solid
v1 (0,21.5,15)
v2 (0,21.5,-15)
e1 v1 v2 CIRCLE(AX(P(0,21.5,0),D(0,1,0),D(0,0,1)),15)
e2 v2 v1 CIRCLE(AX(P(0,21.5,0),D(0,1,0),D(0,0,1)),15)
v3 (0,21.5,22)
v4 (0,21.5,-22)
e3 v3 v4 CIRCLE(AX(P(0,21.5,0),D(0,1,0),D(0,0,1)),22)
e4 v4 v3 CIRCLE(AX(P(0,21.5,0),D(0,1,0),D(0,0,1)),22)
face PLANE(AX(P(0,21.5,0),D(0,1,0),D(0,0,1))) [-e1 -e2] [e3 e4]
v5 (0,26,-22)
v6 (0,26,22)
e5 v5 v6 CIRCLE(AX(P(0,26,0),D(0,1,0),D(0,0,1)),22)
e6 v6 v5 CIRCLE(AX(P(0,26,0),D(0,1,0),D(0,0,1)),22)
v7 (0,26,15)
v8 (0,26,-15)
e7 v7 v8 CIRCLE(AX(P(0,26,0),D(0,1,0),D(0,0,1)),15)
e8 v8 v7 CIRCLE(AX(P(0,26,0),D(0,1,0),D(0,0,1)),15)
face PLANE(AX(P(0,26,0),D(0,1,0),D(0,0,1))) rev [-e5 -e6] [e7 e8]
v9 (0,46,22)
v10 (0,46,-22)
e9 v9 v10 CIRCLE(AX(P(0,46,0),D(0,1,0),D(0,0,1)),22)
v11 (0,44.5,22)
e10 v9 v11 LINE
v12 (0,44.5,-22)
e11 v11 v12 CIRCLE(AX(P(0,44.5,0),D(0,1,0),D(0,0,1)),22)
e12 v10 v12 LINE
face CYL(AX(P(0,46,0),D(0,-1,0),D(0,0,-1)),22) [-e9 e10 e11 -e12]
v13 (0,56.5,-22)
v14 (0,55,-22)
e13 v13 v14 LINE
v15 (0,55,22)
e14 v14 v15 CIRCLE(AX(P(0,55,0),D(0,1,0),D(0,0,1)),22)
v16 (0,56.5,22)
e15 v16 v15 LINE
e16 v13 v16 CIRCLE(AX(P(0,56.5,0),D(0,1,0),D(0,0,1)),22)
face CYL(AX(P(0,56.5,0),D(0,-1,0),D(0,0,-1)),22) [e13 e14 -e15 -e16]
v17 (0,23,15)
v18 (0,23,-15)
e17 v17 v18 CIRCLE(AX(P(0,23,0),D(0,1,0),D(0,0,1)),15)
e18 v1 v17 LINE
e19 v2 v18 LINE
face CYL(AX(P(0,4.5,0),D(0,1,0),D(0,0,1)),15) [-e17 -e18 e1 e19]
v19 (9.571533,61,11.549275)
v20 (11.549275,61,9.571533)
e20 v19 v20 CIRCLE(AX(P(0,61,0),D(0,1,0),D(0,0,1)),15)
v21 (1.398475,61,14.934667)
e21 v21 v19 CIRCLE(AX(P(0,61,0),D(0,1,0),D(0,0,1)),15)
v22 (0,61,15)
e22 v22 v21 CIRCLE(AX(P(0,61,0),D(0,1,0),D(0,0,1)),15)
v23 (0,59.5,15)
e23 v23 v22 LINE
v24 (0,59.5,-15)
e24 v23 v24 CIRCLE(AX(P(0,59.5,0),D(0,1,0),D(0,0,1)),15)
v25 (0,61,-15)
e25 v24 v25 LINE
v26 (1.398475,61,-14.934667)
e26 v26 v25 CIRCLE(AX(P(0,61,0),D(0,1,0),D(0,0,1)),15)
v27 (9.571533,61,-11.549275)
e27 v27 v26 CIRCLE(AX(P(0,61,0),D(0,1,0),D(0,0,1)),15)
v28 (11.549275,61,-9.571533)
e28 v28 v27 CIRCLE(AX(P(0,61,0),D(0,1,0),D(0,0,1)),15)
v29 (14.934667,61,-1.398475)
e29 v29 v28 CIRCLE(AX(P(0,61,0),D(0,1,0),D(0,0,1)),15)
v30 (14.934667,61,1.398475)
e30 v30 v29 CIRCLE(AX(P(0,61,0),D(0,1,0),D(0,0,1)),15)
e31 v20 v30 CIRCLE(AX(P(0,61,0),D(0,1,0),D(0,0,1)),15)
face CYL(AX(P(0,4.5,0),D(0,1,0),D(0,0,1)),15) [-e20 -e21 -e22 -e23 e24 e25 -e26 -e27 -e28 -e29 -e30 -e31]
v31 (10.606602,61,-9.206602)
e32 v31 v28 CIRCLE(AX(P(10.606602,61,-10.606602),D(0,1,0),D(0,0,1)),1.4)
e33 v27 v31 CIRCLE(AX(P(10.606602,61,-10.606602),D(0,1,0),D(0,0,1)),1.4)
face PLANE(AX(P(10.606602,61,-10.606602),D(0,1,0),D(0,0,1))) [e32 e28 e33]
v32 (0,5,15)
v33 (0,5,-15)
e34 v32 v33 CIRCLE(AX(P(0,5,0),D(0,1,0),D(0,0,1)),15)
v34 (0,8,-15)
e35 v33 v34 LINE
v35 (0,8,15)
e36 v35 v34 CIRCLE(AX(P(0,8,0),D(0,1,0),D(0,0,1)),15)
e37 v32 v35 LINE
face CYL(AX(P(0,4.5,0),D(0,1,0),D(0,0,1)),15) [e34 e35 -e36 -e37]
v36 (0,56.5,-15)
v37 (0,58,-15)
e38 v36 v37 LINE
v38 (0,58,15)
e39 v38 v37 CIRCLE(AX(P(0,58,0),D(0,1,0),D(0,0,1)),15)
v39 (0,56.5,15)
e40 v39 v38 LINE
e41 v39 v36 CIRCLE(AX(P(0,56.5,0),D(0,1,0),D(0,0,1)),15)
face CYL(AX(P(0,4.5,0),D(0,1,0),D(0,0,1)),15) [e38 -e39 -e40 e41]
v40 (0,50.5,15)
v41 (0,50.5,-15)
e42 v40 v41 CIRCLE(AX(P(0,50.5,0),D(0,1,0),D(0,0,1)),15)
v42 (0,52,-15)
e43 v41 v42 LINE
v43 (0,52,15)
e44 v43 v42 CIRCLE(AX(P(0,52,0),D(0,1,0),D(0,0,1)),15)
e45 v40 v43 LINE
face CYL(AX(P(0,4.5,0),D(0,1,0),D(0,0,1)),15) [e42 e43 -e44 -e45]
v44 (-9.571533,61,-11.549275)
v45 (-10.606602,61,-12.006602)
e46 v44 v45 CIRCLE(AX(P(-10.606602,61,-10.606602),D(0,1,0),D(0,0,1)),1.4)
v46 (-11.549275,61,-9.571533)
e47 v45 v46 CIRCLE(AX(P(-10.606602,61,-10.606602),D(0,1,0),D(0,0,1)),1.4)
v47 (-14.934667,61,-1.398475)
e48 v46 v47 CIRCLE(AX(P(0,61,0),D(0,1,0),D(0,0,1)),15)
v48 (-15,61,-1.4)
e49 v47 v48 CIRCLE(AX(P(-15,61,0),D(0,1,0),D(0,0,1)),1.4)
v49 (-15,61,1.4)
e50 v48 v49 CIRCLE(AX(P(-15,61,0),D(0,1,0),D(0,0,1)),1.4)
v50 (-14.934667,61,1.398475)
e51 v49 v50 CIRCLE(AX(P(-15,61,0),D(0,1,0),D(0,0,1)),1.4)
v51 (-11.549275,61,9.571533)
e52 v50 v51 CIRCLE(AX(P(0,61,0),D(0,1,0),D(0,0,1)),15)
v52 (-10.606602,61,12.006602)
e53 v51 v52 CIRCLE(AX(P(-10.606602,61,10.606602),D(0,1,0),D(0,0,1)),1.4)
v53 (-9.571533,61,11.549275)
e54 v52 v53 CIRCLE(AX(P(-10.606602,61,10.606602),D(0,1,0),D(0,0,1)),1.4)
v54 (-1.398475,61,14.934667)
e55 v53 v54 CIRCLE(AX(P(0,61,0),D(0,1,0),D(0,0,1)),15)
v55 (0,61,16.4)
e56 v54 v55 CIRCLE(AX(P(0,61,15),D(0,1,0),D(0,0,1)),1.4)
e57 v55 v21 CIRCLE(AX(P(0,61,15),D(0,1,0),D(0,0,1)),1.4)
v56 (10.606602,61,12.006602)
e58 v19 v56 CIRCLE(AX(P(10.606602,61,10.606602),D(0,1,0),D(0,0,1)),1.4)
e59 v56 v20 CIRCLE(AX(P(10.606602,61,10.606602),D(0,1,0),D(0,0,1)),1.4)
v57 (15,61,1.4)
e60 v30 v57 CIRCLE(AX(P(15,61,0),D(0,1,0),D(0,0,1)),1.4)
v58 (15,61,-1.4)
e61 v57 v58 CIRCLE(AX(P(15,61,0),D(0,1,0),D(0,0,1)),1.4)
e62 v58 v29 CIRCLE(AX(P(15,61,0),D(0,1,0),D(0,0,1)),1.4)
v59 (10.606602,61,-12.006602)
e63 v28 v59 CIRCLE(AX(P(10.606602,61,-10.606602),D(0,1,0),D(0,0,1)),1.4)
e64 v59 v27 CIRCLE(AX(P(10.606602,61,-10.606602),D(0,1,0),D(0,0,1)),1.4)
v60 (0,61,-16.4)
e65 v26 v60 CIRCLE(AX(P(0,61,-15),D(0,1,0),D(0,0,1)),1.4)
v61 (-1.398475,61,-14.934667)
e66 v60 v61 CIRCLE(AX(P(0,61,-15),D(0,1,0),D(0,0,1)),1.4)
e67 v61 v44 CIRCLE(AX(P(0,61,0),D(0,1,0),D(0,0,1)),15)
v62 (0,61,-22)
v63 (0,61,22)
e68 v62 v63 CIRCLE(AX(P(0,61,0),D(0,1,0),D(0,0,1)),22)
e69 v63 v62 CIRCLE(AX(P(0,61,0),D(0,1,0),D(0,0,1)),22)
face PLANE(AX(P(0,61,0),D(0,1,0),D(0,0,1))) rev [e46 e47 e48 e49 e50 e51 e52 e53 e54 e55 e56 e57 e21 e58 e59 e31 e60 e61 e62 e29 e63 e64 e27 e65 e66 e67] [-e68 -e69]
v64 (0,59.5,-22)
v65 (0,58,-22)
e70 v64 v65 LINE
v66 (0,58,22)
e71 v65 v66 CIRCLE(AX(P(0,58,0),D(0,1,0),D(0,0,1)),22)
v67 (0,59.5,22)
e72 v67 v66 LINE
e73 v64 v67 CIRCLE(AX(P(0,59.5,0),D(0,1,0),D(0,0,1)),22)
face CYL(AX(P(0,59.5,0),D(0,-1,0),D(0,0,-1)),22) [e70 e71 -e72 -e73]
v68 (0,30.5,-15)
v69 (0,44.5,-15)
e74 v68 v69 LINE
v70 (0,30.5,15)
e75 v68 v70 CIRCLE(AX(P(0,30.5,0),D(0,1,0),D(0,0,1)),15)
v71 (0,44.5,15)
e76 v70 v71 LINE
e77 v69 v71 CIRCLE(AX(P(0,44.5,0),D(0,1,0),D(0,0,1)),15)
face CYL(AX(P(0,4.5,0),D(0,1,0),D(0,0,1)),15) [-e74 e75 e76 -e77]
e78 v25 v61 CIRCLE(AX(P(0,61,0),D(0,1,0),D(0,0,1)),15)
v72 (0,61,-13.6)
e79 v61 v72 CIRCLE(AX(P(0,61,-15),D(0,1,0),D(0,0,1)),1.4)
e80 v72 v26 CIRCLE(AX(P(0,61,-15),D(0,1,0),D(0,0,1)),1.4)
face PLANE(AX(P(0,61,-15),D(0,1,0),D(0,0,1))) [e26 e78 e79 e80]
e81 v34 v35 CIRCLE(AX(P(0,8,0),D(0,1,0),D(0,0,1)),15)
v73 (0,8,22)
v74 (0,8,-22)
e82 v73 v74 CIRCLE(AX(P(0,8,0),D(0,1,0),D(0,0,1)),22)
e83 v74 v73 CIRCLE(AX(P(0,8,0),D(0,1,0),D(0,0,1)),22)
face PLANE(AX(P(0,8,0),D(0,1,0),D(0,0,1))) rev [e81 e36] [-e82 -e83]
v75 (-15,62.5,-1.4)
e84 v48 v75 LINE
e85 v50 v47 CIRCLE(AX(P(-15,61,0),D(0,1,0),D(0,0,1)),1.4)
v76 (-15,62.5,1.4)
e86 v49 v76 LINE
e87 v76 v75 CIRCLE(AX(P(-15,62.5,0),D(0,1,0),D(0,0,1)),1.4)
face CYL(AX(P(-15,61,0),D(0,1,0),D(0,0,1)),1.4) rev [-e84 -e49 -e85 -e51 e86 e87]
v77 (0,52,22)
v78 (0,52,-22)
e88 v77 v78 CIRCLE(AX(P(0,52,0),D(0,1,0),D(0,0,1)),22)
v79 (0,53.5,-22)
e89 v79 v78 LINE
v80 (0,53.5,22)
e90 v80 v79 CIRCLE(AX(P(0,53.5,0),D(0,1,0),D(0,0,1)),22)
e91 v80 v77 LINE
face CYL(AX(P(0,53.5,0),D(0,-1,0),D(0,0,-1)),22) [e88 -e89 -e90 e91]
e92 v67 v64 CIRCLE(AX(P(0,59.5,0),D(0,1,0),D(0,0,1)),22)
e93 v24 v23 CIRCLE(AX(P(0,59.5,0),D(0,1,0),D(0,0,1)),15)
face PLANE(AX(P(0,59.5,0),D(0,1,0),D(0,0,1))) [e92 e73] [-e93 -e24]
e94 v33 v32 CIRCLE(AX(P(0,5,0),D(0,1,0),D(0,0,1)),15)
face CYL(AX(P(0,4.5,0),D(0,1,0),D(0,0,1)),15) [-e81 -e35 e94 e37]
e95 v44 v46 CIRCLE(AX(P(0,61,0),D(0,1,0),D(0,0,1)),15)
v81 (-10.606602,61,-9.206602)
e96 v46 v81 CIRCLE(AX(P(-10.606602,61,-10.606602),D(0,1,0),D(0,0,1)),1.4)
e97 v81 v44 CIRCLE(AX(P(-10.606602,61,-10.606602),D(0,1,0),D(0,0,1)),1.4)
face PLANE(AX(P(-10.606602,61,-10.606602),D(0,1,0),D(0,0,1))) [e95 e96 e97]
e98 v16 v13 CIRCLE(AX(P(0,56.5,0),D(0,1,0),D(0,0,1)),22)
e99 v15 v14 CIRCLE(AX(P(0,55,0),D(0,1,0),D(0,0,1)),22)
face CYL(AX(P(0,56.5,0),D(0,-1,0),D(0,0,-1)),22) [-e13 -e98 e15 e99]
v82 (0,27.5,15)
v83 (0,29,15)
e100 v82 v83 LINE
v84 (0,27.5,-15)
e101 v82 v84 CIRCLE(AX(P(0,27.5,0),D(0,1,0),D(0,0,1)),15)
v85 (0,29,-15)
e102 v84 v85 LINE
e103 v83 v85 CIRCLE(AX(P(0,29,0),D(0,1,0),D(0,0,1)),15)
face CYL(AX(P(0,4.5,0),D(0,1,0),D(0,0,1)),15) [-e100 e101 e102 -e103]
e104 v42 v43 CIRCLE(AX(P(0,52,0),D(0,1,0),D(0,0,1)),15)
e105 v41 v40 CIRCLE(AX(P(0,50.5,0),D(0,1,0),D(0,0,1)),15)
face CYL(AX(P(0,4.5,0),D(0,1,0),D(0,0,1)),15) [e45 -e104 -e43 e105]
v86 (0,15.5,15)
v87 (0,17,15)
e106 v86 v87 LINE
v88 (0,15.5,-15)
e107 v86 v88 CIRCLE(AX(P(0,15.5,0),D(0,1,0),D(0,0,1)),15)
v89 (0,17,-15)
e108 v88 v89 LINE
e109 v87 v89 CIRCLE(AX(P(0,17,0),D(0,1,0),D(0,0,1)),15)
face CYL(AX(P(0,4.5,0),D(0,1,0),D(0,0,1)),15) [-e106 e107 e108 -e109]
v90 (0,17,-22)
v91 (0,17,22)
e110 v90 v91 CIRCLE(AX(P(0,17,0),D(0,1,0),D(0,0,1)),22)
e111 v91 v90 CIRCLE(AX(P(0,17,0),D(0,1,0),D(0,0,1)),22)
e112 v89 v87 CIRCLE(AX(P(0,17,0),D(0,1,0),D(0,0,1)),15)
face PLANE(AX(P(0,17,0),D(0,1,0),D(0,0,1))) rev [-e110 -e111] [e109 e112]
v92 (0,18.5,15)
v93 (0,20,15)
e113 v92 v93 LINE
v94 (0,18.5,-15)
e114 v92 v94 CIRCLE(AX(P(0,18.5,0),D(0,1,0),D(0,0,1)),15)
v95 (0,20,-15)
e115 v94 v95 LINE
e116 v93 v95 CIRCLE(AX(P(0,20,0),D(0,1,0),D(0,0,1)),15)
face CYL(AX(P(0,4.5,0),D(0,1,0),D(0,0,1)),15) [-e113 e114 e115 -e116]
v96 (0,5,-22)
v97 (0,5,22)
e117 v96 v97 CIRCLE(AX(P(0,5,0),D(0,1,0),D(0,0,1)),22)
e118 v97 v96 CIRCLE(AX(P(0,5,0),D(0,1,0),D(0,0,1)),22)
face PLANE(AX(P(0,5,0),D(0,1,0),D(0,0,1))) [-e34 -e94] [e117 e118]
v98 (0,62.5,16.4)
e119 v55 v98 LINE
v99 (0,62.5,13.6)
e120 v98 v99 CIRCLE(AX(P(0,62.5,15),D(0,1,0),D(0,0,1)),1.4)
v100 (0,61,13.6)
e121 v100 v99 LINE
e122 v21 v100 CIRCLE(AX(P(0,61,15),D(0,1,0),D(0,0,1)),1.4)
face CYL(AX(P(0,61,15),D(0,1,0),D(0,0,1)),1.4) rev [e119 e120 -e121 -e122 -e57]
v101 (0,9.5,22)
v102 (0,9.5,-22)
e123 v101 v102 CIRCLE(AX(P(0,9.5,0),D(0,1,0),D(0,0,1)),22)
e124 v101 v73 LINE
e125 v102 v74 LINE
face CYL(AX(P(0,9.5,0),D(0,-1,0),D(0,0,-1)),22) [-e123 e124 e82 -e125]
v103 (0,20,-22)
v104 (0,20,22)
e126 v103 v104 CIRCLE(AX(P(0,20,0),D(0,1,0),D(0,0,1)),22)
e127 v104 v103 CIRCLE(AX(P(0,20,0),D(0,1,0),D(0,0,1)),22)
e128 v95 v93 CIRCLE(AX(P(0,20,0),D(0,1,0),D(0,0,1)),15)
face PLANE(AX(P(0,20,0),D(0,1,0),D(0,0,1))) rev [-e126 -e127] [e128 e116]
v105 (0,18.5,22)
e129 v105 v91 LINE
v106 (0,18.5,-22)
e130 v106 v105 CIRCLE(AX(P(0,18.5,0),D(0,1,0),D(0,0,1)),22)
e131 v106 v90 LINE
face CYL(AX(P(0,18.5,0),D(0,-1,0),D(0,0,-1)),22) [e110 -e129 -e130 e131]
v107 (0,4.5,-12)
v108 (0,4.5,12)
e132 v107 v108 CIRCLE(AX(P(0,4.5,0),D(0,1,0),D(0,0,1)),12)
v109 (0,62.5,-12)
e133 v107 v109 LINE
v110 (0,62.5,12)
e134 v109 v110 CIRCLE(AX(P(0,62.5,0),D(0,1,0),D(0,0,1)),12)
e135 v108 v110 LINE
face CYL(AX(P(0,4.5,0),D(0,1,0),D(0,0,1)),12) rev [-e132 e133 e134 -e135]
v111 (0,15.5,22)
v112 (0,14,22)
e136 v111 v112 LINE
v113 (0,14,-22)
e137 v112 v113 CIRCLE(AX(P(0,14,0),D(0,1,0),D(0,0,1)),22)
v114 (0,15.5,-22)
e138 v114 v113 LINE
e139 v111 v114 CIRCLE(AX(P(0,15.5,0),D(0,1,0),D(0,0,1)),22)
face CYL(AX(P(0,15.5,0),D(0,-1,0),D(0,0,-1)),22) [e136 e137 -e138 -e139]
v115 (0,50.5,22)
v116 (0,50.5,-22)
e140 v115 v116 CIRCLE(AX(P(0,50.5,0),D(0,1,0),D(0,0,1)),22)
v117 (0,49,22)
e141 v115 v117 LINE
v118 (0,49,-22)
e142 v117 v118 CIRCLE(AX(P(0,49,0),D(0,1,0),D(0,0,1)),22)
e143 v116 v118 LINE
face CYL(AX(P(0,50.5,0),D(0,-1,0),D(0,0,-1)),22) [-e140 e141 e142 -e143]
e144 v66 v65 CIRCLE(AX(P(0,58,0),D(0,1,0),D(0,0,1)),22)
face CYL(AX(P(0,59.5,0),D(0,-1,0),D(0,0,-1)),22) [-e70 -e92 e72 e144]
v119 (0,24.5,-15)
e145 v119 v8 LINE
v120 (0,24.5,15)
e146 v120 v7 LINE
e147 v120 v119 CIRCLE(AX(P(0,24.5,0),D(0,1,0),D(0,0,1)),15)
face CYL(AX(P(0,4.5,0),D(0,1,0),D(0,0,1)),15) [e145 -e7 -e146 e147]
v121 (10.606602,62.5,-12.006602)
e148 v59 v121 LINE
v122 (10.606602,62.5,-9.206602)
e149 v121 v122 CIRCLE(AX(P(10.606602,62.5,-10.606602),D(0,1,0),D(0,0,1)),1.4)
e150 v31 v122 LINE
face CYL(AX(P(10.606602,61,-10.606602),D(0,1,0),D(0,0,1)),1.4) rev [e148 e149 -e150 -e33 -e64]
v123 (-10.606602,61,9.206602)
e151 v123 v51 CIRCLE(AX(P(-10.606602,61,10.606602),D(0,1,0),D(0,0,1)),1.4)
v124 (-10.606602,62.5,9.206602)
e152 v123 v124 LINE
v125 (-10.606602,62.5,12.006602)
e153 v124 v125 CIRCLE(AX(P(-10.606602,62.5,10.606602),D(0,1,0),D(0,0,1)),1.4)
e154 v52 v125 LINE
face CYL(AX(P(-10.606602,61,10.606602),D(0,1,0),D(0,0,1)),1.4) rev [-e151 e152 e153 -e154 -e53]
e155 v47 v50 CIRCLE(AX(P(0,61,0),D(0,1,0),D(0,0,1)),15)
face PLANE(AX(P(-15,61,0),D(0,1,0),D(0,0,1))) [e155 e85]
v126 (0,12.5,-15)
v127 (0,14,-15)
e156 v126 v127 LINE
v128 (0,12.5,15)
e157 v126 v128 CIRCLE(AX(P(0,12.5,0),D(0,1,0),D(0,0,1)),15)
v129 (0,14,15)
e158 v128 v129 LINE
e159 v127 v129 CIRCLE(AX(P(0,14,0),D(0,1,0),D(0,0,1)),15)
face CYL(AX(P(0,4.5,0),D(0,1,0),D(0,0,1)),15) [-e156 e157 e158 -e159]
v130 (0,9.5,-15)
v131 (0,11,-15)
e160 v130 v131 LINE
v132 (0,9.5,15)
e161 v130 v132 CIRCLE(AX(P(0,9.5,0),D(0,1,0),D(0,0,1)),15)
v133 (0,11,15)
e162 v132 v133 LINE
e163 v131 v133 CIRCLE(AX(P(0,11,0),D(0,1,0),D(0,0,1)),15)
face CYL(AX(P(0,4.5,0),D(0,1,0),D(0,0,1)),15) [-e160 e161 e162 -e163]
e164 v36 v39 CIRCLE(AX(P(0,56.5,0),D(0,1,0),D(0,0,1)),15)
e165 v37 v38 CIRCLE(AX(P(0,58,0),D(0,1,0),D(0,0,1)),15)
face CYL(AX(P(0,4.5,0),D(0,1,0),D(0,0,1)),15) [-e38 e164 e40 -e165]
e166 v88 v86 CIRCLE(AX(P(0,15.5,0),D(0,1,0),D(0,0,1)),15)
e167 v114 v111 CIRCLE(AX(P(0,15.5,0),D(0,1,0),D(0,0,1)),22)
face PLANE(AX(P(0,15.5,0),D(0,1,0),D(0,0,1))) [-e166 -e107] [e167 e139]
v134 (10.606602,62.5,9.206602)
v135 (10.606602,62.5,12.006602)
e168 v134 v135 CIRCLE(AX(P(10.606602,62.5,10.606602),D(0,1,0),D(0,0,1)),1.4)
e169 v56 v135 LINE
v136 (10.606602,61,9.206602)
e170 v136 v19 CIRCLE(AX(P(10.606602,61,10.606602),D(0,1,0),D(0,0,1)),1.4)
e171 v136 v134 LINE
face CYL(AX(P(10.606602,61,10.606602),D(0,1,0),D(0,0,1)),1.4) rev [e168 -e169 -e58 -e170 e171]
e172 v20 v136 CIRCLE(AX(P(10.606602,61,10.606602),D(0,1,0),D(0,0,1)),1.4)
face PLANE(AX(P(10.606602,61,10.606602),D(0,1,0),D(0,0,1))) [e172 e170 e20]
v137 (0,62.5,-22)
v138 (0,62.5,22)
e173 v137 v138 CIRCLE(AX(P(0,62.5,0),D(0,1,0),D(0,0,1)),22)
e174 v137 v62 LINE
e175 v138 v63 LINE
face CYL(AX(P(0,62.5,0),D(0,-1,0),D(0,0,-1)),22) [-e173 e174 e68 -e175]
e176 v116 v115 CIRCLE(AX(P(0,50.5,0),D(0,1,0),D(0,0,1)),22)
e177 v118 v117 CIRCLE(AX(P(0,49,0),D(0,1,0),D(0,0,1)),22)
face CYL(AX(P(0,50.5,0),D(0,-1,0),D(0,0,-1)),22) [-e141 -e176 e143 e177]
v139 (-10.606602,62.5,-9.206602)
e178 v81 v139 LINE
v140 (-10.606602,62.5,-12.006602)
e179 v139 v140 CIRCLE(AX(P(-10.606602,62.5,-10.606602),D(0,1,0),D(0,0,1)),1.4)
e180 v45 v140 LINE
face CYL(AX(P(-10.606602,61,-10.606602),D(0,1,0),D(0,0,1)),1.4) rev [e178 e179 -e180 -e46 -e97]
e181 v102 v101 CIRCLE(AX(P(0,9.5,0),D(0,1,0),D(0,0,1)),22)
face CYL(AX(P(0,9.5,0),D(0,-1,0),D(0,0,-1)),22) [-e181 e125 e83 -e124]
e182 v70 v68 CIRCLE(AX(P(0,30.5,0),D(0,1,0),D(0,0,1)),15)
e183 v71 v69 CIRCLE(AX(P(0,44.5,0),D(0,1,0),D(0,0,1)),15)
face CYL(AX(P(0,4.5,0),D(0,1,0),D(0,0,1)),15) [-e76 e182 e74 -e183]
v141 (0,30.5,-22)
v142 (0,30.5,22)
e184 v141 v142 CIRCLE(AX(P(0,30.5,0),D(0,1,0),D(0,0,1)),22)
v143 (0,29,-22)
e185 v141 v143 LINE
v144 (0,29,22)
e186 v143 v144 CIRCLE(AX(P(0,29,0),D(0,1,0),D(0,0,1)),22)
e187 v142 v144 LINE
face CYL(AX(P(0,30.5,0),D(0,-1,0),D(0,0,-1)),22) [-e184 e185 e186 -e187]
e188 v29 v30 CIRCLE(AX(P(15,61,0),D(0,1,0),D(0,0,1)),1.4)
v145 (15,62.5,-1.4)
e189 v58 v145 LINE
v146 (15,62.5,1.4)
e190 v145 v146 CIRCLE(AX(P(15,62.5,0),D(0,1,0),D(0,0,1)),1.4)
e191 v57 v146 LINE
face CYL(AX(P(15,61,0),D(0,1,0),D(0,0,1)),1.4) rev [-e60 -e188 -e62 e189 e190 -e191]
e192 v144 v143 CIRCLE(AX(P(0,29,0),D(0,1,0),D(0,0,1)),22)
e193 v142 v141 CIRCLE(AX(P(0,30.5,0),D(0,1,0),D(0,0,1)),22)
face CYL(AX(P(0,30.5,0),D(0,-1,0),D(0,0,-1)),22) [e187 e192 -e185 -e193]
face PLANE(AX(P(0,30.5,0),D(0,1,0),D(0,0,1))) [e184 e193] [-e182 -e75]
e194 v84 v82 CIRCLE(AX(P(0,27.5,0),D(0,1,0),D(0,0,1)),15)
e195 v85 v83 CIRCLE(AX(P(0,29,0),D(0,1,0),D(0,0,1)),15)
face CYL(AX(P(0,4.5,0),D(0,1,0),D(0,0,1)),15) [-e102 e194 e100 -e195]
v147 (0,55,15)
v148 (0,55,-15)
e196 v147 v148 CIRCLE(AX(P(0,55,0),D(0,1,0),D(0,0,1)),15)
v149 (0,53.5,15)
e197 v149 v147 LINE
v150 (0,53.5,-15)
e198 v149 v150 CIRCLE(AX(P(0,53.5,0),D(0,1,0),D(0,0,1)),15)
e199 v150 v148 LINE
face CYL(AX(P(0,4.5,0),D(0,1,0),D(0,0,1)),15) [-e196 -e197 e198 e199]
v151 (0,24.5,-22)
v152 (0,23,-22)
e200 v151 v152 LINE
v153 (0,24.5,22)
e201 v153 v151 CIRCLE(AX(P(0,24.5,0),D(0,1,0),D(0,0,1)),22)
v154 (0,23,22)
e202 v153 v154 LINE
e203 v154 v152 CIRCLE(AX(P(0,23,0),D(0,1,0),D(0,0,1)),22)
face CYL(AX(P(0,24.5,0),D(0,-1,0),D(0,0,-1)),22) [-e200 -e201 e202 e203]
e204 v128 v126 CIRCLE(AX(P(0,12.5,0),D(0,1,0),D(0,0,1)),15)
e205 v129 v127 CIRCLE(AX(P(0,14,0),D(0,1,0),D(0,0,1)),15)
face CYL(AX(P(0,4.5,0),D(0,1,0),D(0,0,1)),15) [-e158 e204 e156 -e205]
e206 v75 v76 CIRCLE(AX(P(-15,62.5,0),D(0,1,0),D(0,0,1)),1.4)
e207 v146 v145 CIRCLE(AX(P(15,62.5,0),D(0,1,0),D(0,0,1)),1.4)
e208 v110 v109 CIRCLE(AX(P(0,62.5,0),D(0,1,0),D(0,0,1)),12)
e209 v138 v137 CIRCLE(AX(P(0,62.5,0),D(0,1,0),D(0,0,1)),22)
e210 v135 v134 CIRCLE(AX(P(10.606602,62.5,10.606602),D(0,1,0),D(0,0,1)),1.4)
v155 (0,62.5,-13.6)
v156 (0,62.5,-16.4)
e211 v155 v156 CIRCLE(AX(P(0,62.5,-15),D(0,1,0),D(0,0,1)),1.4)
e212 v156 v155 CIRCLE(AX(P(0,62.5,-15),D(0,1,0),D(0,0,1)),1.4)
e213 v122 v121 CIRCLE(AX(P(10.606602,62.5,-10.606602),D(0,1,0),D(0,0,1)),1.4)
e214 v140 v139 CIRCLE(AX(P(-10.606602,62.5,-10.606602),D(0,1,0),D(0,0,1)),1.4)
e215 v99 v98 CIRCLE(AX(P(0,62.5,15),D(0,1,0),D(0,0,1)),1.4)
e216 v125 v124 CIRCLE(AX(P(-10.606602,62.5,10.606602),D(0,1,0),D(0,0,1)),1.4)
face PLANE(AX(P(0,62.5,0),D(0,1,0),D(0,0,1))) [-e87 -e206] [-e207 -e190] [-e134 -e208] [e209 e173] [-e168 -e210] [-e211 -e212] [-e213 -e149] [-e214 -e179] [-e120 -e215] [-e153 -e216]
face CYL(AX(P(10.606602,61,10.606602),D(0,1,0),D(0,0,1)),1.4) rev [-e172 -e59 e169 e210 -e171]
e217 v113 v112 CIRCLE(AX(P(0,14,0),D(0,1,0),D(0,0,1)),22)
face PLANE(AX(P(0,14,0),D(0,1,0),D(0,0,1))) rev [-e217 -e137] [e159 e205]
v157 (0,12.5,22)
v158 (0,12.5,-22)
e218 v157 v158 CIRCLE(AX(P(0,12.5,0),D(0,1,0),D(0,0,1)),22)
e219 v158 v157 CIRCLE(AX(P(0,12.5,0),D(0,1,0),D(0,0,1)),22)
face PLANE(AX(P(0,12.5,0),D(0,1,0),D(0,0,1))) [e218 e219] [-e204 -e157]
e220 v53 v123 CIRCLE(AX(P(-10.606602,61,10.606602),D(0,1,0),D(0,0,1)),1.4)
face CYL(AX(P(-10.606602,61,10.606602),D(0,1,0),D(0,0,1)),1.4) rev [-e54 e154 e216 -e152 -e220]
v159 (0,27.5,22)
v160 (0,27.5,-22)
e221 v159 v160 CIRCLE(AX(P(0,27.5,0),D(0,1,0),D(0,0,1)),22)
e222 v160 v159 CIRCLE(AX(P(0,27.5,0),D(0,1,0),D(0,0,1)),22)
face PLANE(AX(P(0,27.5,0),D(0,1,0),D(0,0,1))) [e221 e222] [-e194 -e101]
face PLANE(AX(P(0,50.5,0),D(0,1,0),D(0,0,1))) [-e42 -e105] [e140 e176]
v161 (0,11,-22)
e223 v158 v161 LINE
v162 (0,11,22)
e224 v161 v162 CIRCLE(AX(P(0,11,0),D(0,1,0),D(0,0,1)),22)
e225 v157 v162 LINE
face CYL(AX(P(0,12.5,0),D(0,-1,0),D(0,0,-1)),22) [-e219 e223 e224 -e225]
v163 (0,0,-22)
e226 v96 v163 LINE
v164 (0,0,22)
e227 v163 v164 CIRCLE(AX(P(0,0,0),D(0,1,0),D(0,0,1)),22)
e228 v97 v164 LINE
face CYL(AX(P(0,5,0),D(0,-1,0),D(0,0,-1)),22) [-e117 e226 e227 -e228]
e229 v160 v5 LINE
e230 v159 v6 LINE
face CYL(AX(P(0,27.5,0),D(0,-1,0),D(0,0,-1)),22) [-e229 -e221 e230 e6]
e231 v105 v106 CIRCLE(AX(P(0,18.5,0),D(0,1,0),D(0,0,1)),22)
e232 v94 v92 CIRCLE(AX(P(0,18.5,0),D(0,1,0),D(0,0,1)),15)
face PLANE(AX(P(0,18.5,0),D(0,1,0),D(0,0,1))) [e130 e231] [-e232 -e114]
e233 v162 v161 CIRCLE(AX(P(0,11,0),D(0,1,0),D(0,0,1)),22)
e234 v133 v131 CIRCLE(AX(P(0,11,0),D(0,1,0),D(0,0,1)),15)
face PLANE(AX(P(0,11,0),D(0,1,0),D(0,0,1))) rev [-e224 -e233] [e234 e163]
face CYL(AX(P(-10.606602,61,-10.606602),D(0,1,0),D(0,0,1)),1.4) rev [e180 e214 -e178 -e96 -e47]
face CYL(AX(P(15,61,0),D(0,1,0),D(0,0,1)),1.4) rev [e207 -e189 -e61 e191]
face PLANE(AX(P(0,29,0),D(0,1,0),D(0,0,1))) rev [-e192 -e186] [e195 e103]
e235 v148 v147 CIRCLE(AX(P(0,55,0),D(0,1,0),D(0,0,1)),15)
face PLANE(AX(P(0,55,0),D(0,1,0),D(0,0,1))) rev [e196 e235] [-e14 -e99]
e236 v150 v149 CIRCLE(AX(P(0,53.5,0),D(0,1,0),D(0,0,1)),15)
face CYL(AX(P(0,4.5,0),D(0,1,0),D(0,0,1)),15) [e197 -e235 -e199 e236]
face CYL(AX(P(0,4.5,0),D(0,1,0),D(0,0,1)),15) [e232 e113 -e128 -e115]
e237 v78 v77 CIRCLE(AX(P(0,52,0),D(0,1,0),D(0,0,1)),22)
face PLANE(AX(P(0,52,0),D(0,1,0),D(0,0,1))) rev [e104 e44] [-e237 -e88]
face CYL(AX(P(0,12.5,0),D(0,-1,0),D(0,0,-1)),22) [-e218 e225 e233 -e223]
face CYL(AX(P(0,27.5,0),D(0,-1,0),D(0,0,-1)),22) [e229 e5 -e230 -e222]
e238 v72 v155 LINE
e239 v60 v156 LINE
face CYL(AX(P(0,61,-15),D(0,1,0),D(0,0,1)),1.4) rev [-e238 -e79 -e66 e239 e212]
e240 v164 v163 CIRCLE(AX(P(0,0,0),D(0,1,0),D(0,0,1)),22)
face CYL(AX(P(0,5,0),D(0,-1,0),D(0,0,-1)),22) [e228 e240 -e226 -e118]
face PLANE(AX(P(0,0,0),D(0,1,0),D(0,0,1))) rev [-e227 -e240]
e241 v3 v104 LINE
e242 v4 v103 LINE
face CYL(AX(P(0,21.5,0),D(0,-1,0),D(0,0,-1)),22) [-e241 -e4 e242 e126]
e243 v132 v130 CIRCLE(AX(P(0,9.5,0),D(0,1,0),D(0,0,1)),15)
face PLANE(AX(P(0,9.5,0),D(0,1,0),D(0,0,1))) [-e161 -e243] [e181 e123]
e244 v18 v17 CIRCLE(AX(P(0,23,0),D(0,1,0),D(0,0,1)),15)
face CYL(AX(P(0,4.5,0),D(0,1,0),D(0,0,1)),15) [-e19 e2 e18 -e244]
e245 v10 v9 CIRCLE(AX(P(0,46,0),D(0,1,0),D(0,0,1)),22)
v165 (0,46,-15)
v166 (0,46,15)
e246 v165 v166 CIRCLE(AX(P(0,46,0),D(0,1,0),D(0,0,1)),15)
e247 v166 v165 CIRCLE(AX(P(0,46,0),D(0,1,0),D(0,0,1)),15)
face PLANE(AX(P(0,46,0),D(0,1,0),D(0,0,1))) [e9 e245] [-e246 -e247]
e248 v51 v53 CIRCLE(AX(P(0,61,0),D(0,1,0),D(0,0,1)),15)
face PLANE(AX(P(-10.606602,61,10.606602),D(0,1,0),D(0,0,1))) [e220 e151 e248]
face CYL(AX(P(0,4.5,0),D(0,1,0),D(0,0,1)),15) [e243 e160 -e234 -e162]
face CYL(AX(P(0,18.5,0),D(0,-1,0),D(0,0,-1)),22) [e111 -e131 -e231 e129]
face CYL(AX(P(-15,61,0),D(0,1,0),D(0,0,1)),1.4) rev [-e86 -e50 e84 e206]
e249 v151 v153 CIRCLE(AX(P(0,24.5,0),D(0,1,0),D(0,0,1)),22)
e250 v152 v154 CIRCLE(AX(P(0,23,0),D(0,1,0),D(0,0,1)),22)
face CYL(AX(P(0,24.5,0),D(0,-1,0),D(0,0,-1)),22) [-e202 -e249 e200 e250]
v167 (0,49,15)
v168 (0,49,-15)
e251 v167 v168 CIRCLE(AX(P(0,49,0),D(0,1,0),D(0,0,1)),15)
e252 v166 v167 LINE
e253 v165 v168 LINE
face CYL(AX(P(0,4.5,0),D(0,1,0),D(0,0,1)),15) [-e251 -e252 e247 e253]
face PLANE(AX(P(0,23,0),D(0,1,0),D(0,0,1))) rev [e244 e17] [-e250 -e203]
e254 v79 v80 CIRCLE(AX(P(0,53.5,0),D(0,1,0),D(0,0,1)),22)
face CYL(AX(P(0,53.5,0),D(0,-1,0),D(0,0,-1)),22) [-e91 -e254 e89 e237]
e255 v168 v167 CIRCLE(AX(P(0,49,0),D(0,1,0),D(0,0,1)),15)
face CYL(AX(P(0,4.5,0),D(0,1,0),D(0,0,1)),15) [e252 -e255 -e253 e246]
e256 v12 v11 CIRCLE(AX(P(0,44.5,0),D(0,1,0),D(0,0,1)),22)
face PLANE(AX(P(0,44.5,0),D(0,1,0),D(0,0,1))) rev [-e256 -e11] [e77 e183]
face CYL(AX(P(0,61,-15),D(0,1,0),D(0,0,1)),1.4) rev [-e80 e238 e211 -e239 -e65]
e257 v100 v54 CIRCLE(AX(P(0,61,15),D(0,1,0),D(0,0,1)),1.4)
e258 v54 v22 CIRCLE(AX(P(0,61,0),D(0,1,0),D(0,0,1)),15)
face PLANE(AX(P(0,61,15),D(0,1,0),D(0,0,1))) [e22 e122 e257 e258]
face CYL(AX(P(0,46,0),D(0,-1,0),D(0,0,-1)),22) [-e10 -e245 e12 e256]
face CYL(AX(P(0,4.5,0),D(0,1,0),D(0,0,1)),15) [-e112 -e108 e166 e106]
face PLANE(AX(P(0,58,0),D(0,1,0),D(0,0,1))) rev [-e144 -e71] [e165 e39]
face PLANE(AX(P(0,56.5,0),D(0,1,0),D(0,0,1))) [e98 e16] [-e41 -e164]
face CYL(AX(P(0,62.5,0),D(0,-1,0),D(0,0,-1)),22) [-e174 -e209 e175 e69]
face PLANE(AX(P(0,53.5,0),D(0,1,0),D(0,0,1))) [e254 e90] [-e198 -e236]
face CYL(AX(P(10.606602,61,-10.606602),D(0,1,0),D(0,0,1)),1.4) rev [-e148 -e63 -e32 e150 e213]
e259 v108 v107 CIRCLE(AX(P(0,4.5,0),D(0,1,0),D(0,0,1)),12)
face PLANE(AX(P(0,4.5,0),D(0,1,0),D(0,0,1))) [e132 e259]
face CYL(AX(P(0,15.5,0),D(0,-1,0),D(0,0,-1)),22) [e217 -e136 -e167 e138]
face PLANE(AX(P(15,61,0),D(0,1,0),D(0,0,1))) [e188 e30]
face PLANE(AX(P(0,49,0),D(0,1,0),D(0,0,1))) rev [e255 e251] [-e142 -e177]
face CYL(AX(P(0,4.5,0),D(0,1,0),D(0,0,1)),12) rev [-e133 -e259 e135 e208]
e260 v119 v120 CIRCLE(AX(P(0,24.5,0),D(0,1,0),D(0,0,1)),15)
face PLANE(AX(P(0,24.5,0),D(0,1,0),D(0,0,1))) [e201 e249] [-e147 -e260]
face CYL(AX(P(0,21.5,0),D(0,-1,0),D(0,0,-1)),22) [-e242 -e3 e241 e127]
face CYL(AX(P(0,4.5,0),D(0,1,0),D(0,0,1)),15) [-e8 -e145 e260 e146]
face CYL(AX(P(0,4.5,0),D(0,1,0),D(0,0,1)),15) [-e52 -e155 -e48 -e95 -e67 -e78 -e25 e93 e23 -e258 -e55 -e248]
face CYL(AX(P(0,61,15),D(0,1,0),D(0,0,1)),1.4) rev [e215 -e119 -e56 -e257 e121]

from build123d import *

# Parameters (mm, degrees)
BASE_DISC_SKETCH_R     = 22
BASE_DISC_DEPTH        = 5
LOWER_FIN_1_SKETCH_R   = 22
LOWER_FIN_1_DEPTH      = 1.5
LOWER_FIN_2_SKETCH_R   = 22
LOWER_FIN_2_DEPTH      = 1.5
LOWER_FIN_3_SKETCH_R   = 22
LOWER_FIN_3_DEPTH      = 1.5
LOWER_FIN_4_SKETCH_R   = 22
LOWER_FIN_4_DEPTH      = 1.5
LOWER_FIN_5_SKETCH_R   = 22
LOWER_FIN_5_DEPTH      = 1.5
LOWER_FIN_6_SKETCH_R   = 22
LOWER_FIN_6_DEPTH      = 1.5
LOWER_FIN_7_SKETCH_R   = 22
LOWER_FIN_7_DEPTH      = 1.5
LOWER_FIN_8_SKETCH_R   = 22
LOWER_FIN_8_DEPTH      = 1.5
UPPER_FIN_1_SKETCH_R   = 22
UPPER_FIN_1_DEPTH      = 1.5
UPPER_FIN_2_SKETCH_R   = 22
UPPER_FIN_2_DEPTH      = 1.5
UPPER_FIN_3_SKETCH_R   = 22
UPPER_FIN_3_DEPTH      = 1.5
UPPER_FIN_4_SKETCH_R   = 22
UPPER_FIN_4_DEPTH      = 1.5
UPPER_FIN_5_SKETCH_R   = 22
UPPER_FIN_5_DEPTH      = 1.5
UPPER_FIN_6_SKETCH_R   = 22
UPPER_FIN_6_DEPTH      = 1.5
CORE_BOSS_SKETCH_R     = 12
CORE_BOSS_58MM_DEPTH   = 58
HUB_BOSS_SKETCH_R      = 15
HUB_BOSS_58MM_DEPTH    = 58
CENTRAL_BORE_SKETCH_R  = 12
CENTRAL_BORE_DEPTH     = 58
BOLT_HOLES_8X_SKETCH_R = 1.4
BOLT_HOLES_8X_DEPTH    = 1.5


with BuildPart() as part:
    # Base Disc Sketch → Base Disc (new body)
    with BuildSketch(Plane(origin=(0, 0, 0), x_dir=(1, 0, 0), z_dir=(0, 1, 0))):
        with Locations(Location((0, 0, 0), (0, 0, 270))):
            Circle(BASE_DISC_SKETCH_R)
    extrude(amount=BASE_DISC_DEPTH)



with BuildPart() as body_2:
    # Lower Fin 1 Sketch → Lower Fin 1 (new body)
    with BuildSketch(Plane(origin=(0, 8, 0), x_dir=(1, 0, 0), z_dir=(0, 1, 0))):
        with Locations(Location((0, 0, 0), (0, 0, 270))):
            Circle(LOWER_FIN_1_SKETCH_R)
    extrude(amount=LOWER_FIN_1_DEPTH)


with BuildPart() as body_3:
    # Lower Fin 2 Sketch → Lower Fin 2 (new body)
    with BuildSketch(Plane(origin=(0, 11, 0), x_dir=(1, 0, 0), z_dir=(0, 1, 0))):
        with Locations(Location((0, 0, 0), (0, 0, 270))):
            Circle(LOWER_FIN_2_SKETCH_R)
    extrude(amount=LOWER_FIN_2_DEPTH)


with BuildPart() as body_4:
    # Lower Fin 3 Sketch → Lower Fin 3 (new body)
    with BuildSketch(Plane(origin=(0, 14, 0), x_dir=(1, 0, 0), z_dir=(0, 1, 0))):
        with Locations(Location((0, 0, 0), (0, 0, 270))):
            Circle(LOWER_FIN_3_SKETCH_R)
    extrude(amount=LOWER_FIN_3_DEPTH)


with BuildPart() as body_5:
    # Lower Fin 4 Sketch → Lower Fin 4 (new body)
    with BuildSketch(Plane(origin=(0, 17, 0), x_dir=(1, 0, 0), z_dir=(0, 1, 0))):
        with Locations(Location((0, 0, 0), (0, 0, 270))):
            Circle(LOWER_FIN_4_SKETCH_R)
    extrude(amount=LOWER_FIN_4_DEPTH)


with BuildPart() as body_6:
    # Lower Fin 5 Sketch → Lower Fin 5 (new body)
    with BuildSketch(Plane(origin=(0, 20, 0), x_dir=(1, 0, 0), z_dir=(0, 1, 0))):
        with Locations(Location((0, 0, 0), (0, 0, 270))):
            Circle(LOWER_FIN_5_SKETCH_R)
    extrude(amount=LOWER_FIN_5_DEPTH)


with BuildPart() as body_7:
    # Lower Fin 6 Sketch → Lower Fin 6 (new body)
    with BuildSketch(Plane(origin=(0, 23, 0), x_dir=(1, 0, 0), z_dir=(0, 1, 0))):
        with Locations(Location((0, 0, 0), (0, 0, 270))):
            Circle(LOWER_FIN_6_SKETCH_R)
    extrude(amount=LOWER_FIN_6_DEPTH)


with BuildPart() as body_8:
    # Lower Fin 7 Sketch → Lower Fin 7 (new body)
    with BuildSketch(Plane(origin=(0, 26, 0), x_dir=(1, 0, 0), z_dir=(0, 1, 0))):
        with Locations(Location((0, 0, 0), (0, 0, 270))):
            Circle(LOWER_FIN_7_SKETCH_R)
    extrude(amount=LOWER_FIN_7_DEPTH)


with BuildPart() as body_9:
    # Lower Fin 8 Sketch → Lower Fin 8 (new body)
    with BuildSketch(Plane(origin=(0, 29, 0), x_dir=(1, 0, 0), z_dir=(0, 1, 0))):
        with Locations(Location((0, 0, 0), (0, 0, 270))):
            Circle(LOWER_FIN_8_SKETCH_R)
    extrude(amount=LOWER_FIN_8_DEPTH)


with BuildPart() as body_10:
    # Upper Fin 1 Sketch → Upper Fin 1 (new body)
    with BuildSketch(Plane(origin=(0, 44.5, 0), x_dir=(1, 0, 0), z_dir=(0, 1, 0))):
        with Locations(Location((0, 0, 0), (0, 0, 270))):
            Circle(UPPER_FIN_1_SKETCH_R)
    extrude(amount=UPPER_FIN_1_DEPTH)


with BuildPart() as body_11:
    # Upper Fin 2 Sketch → Upper Fin 2 (new body)
    with BuildSketch(Plane(origin=(0, 49, 0), x_dir=(1, 0, 0), z_dir=(0, 1, 0))):
        with Locations(Location((0, 0, 0), (0, 0, 270))):
            Circle(UPPER_FIN_2_SKETCH_R)
    extrude(amount=UPPER_FIN_2_DEPTH)


with BuildPart() as body_12:
    # Upper Fin 3 Sketch → Upper Fin 3 (new body)
    with BuildSketch(Plane(origin=(0, 52, 0), x_dir=(1, 0, 0), z_dir=(0, 1, 0))):
        with Locations(Location((0, 0, 0), (0, 0, 270))):
            Circle(UPPER_FIN_3_SKETCH_R)
    extrude(amount=UPPER_FIN_3_DEPTH)


with BuildPart() as body_13:
    # Upper Fin 4 Sketch → Upper Fin 4 (new body)
    with BuildSketch(Plane(origin=(0, 55, 0), x_dir=(1, 0, 0), z_dir=(0, 1, 0))):
        with Locations(Location((0, 0, 0), (0, 0, 270))):
            Circle(UPPER_FIN_4_SKETCH_R)
    extrude(amount=UPPER_FIN_4_DEPTH)


with BuildPart() as body_14:
    # Upper Fin 5 Sketch → Upper Fin 5 (new body)
    with BuildSketch(Plane(origin=(0, 58, 0), x_dir=(1, 0, 0), z_dir=(0, 1, 0))):
        with Locations(Location((0, 0, 0), (0, 0, 270))):
            Circle(UPPER_FIN_5_SKETCH_R)
    extrude(amount=UPPER_FIN_5_DEPTH)


with BuildPart() as body_15:
    # Upper Fin 6 Sketch → Upper Fin 6 (new body)
    with BuildSketch(Plane(origin=(0, 61, 0), x_dir=(1, 0, 0), z_dir=(0, 1, 0))):
        with Locations(Location((0, 0, 0), (0, 0, 270))):
            Circle(UPPER_FIN_6_SKETCH_R)
    extrude(amount=UPPER_FIN_6_DEPTH)


with BuildPart() as part_1:
    add(part.part)

    add(body_2.part)  # Core Boss 58mm merges body 2

    add(body_3.part)  # Core Boss 58mm merges body 3

    add(body_4.part)  # Core Boss 58mm merges body 4

    add(body_5.part)  # Core Boss 58mm merges body 5

    add(body_6.part)  # Core Boss 58mm merges body 6

    add(body_7.part)  # Core Boss 58mm merges body 7

    add(body_8.part)  # Core Boss 58mm merges body 8

    add(body_9.part)  # Core Boss 58mm merges body 9

    add(body_10.part)  # Core Boss 58mm merges body 10

    add(body_11.part)  # Core Boss 58mm merges body 11

    add(body_12.part)  # Core Boss 58mm merges body 12

    add(body_13.part)  # Core Boss 58mm merges body 13

    add(body_14.part)  # Core Boss 58mm merges body 14

    add(body_15.part)  # Core Boss 58mm merges body 15
    # Core Boss Sketch → Core Boss 58mm (add)
    with BuildSketch(Plane(origin=(0, 62.5, 0), x_dir=(1, 0, 0), z_dir=(0, 1, 0))):
        with Locations(Location((0, 0, 0), (0, 0, 270))):
            Circle(CORE_BOSS_SKETCH_R)
    extrude(amount=-CORE_BOSS_58MM_DEPTH)

    # Hub Boss Sketch → Hub Boss 58mm (add)
    with BuildSketch(Plane(origin=(0, 62.5, 0), x_dir=(1, 0, 0), z_dir=(0, 1, 0))):
        with Locations(Location((0, 0, 0), (0, 0, 270))):
            Circle(HUB_BOSS_SKETCH_R)
    extrude(amount=-HUB_BOSS_58MM_DEPTH)

    # Central Bore Sketch → Central Bore (cut)
    with BuildSketch(Plane(origin=(0, 62.5, 0), x_dir=(1, 0, 0), z_dir=(0, 1, 0))):
        with Locations(Location((0, 0, 0), (0, 0, 270))):
            Circle(CENTRAL_BORE_SKETCH_R)
    extrude(amount=-CENTRAL_BORE_DEPTH, mode=Mode.SUBTRACT)

    # Bolt Holes 8x Sketch → Bolt Holes 8x (cut)
    with BuildSketch(Plane(origin=(0, 62.5, 0), x_dir=(1, 0, 0), z_dir=(0, 1, 0))):
        with Locations(Location((0, 15, 0), (0, 0, 270))):
            Circle(BOLT_HOLES_8X_SKETCH_R)
        with Locations(Location((10.606601718, 10.606601718, 0), (0, 0, 270))):
            Circle(BOLT_HOLES_8X_SKETCH_R)
        with Locations(Location((15, 0, 0), (0, 0, 270))):
            Circle(BOLT_HOLES_8X_SKETCH_R)
        with Locations(Location((10.606601718, -10.606601718, 0), (0, 0, 270))):
            Circle(BOLT_HOLES_8X_SKETCH_R)
        with Locations(Location((0, -15, 0), (0, 0, 270))):
            Circle(BOLT_HOLES_8X_SKETCH_R)
        with Locations(Location((-10.606601718, -10.606601718, 0), (0, 0, 270))):
            Circle(BOLT_HOLES_8X_SKETCH_R)
        with Locations(Location((-15, 0, 0), (0, 0, 270))):
            Circle(BOLT_HOLES_8X_SKETCH_R)
        with Locations(Location((-10.606601718, 10.606601718, 0), (0, 0, 270))):
            Circle(BOLT_HOLES_8X_SKETCH_R)
    extrude(amount=-BOLT_HOLES_8X_DEPTH, mode=Mode.SUBTRACT)


solid = part_1.part
